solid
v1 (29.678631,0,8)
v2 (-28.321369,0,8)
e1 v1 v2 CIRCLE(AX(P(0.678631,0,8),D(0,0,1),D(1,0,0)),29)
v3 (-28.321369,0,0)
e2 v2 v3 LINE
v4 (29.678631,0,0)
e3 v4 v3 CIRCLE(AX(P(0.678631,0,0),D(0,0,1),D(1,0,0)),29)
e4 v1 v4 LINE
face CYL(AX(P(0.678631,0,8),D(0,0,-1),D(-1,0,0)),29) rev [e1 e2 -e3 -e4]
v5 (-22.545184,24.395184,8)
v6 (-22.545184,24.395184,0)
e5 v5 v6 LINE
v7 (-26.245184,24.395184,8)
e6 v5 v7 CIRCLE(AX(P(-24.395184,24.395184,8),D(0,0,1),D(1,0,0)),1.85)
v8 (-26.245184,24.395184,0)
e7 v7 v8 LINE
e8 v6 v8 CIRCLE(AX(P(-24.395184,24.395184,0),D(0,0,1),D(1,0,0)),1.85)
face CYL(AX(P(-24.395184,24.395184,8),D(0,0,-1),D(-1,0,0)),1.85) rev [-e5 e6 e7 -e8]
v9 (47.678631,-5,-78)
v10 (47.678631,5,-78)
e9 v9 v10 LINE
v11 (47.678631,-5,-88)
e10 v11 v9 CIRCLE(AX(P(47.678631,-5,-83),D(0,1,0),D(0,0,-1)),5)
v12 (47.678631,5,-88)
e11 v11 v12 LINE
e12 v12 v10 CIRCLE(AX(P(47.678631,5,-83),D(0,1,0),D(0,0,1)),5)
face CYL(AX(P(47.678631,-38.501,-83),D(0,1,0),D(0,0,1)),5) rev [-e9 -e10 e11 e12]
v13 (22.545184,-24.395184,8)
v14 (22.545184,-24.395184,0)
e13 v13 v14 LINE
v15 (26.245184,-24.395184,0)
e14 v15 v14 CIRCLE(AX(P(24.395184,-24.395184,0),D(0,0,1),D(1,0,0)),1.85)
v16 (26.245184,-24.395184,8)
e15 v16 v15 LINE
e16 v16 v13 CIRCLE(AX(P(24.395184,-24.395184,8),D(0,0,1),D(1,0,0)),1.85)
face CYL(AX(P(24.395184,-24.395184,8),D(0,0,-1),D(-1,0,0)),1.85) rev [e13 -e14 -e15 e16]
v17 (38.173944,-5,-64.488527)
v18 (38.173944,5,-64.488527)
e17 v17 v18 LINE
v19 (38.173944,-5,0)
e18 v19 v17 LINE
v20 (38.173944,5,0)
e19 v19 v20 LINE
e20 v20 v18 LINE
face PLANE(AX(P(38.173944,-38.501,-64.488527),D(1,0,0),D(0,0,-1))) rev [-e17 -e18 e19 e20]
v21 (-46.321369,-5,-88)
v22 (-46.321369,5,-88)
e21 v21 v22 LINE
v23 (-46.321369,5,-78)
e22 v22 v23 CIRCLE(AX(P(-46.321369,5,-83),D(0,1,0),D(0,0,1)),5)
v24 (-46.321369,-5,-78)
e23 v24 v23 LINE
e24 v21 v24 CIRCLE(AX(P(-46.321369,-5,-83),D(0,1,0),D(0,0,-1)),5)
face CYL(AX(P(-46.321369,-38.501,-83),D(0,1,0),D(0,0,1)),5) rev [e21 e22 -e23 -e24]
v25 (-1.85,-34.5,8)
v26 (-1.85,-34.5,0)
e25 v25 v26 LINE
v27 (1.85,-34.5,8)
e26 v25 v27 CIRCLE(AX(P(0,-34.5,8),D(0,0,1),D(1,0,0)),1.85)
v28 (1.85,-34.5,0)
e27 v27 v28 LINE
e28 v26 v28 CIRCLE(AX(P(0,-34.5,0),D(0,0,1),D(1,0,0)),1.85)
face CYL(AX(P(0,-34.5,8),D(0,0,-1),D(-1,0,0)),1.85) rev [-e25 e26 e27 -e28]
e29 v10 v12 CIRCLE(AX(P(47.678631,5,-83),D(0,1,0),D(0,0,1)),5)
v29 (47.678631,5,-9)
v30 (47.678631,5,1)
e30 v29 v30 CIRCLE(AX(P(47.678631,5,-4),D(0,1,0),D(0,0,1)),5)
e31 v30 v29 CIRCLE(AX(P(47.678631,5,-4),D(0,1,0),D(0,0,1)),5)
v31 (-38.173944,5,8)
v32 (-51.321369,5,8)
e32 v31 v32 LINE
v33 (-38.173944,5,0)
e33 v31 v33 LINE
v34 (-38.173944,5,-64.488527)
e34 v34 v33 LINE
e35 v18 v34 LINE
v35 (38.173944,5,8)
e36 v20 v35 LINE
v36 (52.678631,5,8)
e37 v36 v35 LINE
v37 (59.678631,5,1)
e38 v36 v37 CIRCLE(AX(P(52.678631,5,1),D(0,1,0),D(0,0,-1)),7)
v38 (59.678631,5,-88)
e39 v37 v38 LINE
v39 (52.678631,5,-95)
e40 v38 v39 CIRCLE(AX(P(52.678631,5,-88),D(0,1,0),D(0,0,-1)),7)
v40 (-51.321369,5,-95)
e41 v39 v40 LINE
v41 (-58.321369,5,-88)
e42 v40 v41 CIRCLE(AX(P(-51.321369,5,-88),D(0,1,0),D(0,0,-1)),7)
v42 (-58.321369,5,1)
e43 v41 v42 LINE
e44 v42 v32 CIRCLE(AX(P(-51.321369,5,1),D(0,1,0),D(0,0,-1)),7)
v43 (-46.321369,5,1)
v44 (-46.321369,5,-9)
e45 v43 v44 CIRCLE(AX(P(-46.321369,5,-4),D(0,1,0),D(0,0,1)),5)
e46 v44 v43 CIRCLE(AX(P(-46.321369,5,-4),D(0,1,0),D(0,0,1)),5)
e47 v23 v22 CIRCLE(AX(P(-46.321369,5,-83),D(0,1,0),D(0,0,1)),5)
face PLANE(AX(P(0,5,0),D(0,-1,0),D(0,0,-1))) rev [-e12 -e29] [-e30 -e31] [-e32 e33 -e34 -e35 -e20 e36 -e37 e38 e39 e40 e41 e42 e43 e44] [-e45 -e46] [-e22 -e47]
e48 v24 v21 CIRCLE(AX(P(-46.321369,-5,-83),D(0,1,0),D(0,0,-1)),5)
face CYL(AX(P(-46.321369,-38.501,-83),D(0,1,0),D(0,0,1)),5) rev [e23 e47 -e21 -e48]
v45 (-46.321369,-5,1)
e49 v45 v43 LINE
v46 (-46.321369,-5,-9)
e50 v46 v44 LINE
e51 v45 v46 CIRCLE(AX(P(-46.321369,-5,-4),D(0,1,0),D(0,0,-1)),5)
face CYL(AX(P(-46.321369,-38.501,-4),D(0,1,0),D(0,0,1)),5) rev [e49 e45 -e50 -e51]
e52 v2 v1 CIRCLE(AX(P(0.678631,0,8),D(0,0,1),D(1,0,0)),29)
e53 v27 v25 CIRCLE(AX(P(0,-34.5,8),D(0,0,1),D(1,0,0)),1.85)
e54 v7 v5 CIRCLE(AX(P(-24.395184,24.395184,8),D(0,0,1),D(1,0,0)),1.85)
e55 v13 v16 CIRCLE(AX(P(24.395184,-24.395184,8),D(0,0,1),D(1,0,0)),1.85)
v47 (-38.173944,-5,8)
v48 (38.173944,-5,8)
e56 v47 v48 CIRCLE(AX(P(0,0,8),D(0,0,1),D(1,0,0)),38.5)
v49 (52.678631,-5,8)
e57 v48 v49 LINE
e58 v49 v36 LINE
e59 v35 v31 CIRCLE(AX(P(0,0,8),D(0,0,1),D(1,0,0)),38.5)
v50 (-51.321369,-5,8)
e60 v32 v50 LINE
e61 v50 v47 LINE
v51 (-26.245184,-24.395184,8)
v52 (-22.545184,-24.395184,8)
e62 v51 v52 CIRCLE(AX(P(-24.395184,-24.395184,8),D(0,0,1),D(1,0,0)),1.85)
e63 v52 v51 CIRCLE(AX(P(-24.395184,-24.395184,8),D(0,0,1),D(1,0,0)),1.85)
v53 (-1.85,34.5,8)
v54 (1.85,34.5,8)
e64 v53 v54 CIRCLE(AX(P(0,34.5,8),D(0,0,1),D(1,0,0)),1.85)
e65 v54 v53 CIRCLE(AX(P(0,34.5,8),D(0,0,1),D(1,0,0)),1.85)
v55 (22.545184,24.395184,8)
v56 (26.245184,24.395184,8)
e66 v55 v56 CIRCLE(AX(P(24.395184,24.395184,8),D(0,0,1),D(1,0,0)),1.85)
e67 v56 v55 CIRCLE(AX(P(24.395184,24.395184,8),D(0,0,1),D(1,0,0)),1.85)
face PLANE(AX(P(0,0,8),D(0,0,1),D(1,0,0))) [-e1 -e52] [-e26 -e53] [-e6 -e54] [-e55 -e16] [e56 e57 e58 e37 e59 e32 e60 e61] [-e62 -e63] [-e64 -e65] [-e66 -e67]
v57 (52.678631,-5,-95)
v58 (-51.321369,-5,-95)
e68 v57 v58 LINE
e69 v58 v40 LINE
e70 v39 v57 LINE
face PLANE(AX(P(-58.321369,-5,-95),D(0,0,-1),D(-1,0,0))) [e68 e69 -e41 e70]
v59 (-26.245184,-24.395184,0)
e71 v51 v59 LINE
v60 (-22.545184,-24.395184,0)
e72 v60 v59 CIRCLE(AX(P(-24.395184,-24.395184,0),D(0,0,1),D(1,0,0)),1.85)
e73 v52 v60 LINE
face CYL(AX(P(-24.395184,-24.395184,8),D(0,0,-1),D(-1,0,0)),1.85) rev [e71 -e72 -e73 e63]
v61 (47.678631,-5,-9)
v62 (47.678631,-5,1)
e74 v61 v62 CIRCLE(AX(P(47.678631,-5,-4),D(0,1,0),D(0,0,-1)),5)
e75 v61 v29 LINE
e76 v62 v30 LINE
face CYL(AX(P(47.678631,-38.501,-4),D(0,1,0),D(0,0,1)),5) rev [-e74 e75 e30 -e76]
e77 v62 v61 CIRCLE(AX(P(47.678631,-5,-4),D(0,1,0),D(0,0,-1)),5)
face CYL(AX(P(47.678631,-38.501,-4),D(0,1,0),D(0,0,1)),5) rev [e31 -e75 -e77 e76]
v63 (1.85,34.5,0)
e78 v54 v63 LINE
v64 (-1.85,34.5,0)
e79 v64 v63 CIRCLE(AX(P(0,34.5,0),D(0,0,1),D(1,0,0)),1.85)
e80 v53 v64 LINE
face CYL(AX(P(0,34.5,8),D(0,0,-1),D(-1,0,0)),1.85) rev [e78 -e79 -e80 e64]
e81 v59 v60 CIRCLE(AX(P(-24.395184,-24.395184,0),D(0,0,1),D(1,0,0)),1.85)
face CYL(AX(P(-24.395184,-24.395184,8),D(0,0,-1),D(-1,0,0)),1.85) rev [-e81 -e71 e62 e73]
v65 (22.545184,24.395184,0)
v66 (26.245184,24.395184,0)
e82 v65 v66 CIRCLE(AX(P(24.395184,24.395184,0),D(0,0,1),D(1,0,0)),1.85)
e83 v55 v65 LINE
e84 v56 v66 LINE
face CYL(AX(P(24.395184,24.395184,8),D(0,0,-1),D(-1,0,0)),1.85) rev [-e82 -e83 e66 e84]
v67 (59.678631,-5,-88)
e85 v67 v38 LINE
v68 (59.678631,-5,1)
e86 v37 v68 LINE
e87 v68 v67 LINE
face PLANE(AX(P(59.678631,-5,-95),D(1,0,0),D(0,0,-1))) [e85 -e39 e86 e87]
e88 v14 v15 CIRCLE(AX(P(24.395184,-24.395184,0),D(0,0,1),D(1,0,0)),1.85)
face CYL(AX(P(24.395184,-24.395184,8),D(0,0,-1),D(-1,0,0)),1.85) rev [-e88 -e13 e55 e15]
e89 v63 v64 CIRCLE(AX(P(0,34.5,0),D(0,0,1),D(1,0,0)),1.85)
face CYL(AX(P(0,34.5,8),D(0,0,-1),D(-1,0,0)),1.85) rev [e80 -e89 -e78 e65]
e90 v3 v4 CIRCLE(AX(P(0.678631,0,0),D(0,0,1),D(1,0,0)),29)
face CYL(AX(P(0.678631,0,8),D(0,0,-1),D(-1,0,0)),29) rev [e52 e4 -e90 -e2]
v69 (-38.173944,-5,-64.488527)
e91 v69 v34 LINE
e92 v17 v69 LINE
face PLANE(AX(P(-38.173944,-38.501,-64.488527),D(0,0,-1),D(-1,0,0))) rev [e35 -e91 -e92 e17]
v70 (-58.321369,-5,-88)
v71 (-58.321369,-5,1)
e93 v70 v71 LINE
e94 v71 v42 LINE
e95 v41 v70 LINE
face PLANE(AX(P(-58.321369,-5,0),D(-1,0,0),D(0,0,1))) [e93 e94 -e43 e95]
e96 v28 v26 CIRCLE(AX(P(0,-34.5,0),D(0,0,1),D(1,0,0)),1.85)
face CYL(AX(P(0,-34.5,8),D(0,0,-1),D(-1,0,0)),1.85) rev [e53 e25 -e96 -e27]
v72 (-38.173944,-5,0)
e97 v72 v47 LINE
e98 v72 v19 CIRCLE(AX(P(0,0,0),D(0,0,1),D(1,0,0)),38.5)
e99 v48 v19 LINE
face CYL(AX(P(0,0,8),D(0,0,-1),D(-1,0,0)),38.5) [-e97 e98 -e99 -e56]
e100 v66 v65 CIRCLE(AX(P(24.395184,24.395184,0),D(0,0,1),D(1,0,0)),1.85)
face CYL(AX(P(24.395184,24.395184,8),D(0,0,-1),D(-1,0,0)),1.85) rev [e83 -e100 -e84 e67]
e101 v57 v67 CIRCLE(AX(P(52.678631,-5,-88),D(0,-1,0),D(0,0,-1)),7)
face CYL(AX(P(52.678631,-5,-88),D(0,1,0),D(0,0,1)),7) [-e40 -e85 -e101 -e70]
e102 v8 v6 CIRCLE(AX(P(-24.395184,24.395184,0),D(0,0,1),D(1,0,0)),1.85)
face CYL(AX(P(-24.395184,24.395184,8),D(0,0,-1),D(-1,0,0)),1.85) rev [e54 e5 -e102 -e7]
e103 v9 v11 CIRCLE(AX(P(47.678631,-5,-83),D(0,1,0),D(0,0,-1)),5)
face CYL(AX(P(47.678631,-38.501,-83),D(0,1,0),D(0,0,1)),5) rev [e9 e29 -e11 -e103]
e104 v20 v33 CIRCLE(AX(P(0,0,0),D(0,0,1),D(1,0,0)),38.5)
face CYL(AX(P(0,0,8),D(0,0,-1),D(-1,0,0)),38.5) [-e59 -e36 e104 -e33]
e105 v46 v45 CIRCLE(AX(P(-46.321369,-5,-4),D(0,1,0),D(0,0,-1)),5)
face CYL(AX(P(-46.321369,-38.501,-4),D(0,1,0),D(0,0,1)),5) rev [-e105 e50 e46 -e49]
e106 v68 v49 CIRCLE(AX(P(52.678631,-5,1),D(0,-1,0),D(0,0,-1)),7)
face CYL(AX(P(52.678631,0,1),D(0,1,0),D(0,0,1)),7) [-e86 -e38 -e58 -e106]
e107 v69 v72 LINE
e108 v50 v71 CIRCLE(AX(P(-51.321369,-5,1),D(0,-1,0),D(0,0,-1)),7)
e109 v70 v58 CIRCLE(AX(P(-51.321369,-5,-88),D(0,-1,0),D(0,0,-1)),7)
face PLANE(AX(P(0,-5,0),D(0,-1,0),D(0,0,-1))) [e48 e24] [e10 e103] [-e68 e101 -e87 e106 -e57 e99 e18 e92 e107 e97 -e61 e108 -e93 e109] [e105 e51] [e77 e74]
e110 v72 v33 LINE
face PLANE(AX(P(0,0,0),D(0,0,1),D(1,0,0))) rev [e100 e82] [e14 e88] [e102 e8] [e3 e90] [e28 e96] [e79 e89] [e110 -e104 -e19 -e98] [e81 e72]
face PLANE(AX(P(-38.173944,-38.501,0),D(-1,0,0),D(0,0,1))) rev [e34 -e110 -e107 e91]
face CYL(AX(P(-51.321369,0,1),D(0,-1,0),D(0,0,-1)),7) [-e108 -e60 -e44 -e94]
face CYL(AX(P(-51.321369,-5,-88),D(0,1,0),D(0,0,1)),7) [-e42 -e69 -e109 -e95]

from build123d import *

# Parameters (mm, degrees)
SKETCH2_R                = 38.5
SKETCH2_R_2              = 29
SKETCH2_R_3              = 1.85
BOSS_EXTRUDE1_DEPTH      = 8
BOSS_EXTRUDE2_DEPTH      = 5
BOSS_EXTRUDE2_DEPTH_BACK = 5
SKETCH4_W                = 22.91440569
SKETCH4_H                = 10
SKETCH4_W_2              = 25.697687416
BOSS_EXTRUDE3_DEPTH      = 8
CUT_EXTRUDE1_REACH       = 122.328
SKETCH5_R                = 5
FILLET1_R                = 7
CUT_EXTRUDE2_REACH       = 122.328
SKETCH6_W                = 76.347887986
SKETCH6_H                = 64.488526755


with BuildPart() as part:
    # Sketch2 → Boss-Extrude1 (new body)
    with BuildSketch(Plane.XY):
        Circle(SKETCH2_R)
        with Locations((0.678631435, 0)):
            Circle(SKETCH2_R_2, mode=Mode.SUBTRACT)
        with Locations((0, 34.5)):
            Circle(SKETCH2_R_3, mode=Mode.SUBTRACT)
        with Locations((24.395183951, 24.395183951)):
            Circle(SKETCH2_R_3, mode=Mode.SUBTRACT)
        with Locations((24.395183951, -24.395183951)):
            Circle(SKETCH2_R_3, mode=Mode.SUBTRACT)
        with Locations((0, -34.5)):
            Circle(SKETCH2_R_3, mode=Mode.SUBTRACT)
        with Locations((-24.395183951, -24.395183951)):
            Circle(SKETCH2_R_3, mode=Mode.SUBTRACT)
        with Locations((-24.395183951, 24.395183951)):
            Circle(SKETCH2_R_3, mode=Mode.SUBTRACT)
    extrude(amount=BOSS_EXTRUDE1_DEPTH)

    # Sketch3 → Boss-Extrude2 (add, two sides: drawn at the far end of the back side and taken through both)
    with BuildSketch(Plane(origin=(0, 0, 0), x_dir=(1, 0, 0), z_dir=(0, 1, 0)).offset(-BOSS_EXTRUDE2_DEPTH_BACK)):
        Polygon((-28.321368565, 0), (-38.5, 0), (-58.321368565, 0), (-58.321368565, 67.772616809), (-58.321368565, 95), (59.678631435, 95), (59.678631435, 67.772616809), (59.678631435, 0), (38.5, 0), (29.678631435, 0), (29.678631435, 60), (-28.321368565, 60), align=None)
    extrude(amount=BOSS_EXTRUDE2_DEPTH + BOSS_EXTRUDE2_DEPTH_BACK)

    # Sketch4 → Boss-Extrude3 (add)
    with BuildSketch(Plane.XY):
        with Locations((-46.86416572, 0)):
            Rectangle(SKETCH4_W, SKETCH4_H)
        with Locations((46.829787727, 0)):
            Rectangle(SKETCH4_W_2, SKETCH4_H)
    extrude(amount=BOSS_EXTRUDE3_DEPTH)

    # Sketch5 → Cut-Extrude1 (cut, up to next)
    with BuildSketch(Plane(origin=(0, 5, 0), x_dir=(1, 0, 0), z_dir=(0, 1, 0)), mode=Mode.PRIVATE) as cut_extrude1_sk1:
        with Locations(Location((-46.321368565, 83, 0), (0, 0, 270))):
            Circle(SKETCH5_R)
    cut_extrude1_tool1 = extrude(cut_extrude1_sk1.sketch, amount=-CUT_EXTRUDE1_REACH, mode=Mode.PRIVATE) & part.part
    # Sketch5 → Cut-Extrude1 (cut, up to next)
    with BuildSketch(Plane(origin=(0, 5, 0), x_dir=(1, 0, 0), z_dir=(0, 1, 0)), mode=Mode.PRIVATE) as cut_extrude1_sk2:
        with Locations(Location((-46.321368565, 4, 0), (0, 0, 270))):
            Circle(SKETCH5_R)
    cut_extrude1_tool2 = extrude(cut_extrude1_sk2.sketch, amount=-CUT_EXTRUDE1_REACH, mode=Mode.PRIVATE) & part.part
    # Sketch5 → Cut-Extrude1 (cut, up to next)
    with BuildSketch(Plane(origin=(0, 5, 0), x_dir=(1, 0, 0), z_dir=(0, 1, 0)), mode=Mode.PRIVATE) as cut_extrude1_sk3:
        with Locations(Location((47.678631435, 83, 0), (0, 0, 270))):
            Circle(SKETCH5_R)
    cut_extrude1_tool3 = extrude(cut_extrude1_sk3.sketch, amount=-CUT_EXTRUDE1_REACH, mode=Mode.PRIVATE) & part.part
    # Sketch5 → Cut-Extrude1 (cut, up to next)
    with BuildSketch(Plane(origin=(0, 5, 0), x_dir=(1, 0, 0), z_dir=(0, 1, 0)), mode=Mode.PRIVATE) as cut_extrude1_sk4:
        with Locations(Location((47.678631435, 4, 0), (0, 0, 270))):
            Circle(SKETCH5_R)
    cut_extrude1_tool4 = extrude(cut_extrude1_sk4.sketch, amount=-CUT_EXTRUDE1_REACH, mode=Mode.PRIVATE) & part.part
    add(cut_extrude1_tool1.solids().sort_by_distance((-46.321369, 5, -83))[0], mode=Mode.SUBTRACT)
    add(cut_extrude1_tool2.solids().sort_by_distance((-46.321369, 5, -4))[0], mode=Mode.SUBTRACT)
    add(cut_extrude1_tool3.solids().sort_by_distance((47.678631, 5, -83))[0], mode=Mode.SUBTRACT)
    add(cut_extrude1_tool4.solids().sort_by_distance((47.678631, 5, -4))[0], mode=Mode.SUBTRACT)

    # Fillet1
    fillet1_edges = [part.edges().sort_by_distance(p)[0] for p in [
        (-28.321368565, 0, -60),
        (-58.321368565, 0, -95),
        (59.678631435, 0, -95),
        (29.678631435, 0, -60),
        (-58.321368565, 0, 8),
        (59.678631435, 0, 8),
    ]]
    fillet(fillet1_edges, radius=FILLET1_R)

    # Sketch6 → Cut-Extrude2 (cut, up to next)
    with BuildSketch(Plane(origin=(0, 5, 0), x_dir=(1, 0, 0), z_dir=(0, 1, 0)), mode=Mode.PRIVATE) as cut_extrude2_sk1:
        with Locations((0, 32.244263378)):
            Rectangle(SKETCH6_W, SKETCH6_H)
    cut_extrude2_tool1 = extrude(cut_extrude2_sk1.sketch, amount=-CUT_EXTRUDE2_REACH, mode=Mode.PRIVATE) & part.part
    add(cut_extrude2_tool1.solids().sort_by_distance((0, 5, -32.244263))[0], mode=Mode.SUBTRACT)


solid = part.part
